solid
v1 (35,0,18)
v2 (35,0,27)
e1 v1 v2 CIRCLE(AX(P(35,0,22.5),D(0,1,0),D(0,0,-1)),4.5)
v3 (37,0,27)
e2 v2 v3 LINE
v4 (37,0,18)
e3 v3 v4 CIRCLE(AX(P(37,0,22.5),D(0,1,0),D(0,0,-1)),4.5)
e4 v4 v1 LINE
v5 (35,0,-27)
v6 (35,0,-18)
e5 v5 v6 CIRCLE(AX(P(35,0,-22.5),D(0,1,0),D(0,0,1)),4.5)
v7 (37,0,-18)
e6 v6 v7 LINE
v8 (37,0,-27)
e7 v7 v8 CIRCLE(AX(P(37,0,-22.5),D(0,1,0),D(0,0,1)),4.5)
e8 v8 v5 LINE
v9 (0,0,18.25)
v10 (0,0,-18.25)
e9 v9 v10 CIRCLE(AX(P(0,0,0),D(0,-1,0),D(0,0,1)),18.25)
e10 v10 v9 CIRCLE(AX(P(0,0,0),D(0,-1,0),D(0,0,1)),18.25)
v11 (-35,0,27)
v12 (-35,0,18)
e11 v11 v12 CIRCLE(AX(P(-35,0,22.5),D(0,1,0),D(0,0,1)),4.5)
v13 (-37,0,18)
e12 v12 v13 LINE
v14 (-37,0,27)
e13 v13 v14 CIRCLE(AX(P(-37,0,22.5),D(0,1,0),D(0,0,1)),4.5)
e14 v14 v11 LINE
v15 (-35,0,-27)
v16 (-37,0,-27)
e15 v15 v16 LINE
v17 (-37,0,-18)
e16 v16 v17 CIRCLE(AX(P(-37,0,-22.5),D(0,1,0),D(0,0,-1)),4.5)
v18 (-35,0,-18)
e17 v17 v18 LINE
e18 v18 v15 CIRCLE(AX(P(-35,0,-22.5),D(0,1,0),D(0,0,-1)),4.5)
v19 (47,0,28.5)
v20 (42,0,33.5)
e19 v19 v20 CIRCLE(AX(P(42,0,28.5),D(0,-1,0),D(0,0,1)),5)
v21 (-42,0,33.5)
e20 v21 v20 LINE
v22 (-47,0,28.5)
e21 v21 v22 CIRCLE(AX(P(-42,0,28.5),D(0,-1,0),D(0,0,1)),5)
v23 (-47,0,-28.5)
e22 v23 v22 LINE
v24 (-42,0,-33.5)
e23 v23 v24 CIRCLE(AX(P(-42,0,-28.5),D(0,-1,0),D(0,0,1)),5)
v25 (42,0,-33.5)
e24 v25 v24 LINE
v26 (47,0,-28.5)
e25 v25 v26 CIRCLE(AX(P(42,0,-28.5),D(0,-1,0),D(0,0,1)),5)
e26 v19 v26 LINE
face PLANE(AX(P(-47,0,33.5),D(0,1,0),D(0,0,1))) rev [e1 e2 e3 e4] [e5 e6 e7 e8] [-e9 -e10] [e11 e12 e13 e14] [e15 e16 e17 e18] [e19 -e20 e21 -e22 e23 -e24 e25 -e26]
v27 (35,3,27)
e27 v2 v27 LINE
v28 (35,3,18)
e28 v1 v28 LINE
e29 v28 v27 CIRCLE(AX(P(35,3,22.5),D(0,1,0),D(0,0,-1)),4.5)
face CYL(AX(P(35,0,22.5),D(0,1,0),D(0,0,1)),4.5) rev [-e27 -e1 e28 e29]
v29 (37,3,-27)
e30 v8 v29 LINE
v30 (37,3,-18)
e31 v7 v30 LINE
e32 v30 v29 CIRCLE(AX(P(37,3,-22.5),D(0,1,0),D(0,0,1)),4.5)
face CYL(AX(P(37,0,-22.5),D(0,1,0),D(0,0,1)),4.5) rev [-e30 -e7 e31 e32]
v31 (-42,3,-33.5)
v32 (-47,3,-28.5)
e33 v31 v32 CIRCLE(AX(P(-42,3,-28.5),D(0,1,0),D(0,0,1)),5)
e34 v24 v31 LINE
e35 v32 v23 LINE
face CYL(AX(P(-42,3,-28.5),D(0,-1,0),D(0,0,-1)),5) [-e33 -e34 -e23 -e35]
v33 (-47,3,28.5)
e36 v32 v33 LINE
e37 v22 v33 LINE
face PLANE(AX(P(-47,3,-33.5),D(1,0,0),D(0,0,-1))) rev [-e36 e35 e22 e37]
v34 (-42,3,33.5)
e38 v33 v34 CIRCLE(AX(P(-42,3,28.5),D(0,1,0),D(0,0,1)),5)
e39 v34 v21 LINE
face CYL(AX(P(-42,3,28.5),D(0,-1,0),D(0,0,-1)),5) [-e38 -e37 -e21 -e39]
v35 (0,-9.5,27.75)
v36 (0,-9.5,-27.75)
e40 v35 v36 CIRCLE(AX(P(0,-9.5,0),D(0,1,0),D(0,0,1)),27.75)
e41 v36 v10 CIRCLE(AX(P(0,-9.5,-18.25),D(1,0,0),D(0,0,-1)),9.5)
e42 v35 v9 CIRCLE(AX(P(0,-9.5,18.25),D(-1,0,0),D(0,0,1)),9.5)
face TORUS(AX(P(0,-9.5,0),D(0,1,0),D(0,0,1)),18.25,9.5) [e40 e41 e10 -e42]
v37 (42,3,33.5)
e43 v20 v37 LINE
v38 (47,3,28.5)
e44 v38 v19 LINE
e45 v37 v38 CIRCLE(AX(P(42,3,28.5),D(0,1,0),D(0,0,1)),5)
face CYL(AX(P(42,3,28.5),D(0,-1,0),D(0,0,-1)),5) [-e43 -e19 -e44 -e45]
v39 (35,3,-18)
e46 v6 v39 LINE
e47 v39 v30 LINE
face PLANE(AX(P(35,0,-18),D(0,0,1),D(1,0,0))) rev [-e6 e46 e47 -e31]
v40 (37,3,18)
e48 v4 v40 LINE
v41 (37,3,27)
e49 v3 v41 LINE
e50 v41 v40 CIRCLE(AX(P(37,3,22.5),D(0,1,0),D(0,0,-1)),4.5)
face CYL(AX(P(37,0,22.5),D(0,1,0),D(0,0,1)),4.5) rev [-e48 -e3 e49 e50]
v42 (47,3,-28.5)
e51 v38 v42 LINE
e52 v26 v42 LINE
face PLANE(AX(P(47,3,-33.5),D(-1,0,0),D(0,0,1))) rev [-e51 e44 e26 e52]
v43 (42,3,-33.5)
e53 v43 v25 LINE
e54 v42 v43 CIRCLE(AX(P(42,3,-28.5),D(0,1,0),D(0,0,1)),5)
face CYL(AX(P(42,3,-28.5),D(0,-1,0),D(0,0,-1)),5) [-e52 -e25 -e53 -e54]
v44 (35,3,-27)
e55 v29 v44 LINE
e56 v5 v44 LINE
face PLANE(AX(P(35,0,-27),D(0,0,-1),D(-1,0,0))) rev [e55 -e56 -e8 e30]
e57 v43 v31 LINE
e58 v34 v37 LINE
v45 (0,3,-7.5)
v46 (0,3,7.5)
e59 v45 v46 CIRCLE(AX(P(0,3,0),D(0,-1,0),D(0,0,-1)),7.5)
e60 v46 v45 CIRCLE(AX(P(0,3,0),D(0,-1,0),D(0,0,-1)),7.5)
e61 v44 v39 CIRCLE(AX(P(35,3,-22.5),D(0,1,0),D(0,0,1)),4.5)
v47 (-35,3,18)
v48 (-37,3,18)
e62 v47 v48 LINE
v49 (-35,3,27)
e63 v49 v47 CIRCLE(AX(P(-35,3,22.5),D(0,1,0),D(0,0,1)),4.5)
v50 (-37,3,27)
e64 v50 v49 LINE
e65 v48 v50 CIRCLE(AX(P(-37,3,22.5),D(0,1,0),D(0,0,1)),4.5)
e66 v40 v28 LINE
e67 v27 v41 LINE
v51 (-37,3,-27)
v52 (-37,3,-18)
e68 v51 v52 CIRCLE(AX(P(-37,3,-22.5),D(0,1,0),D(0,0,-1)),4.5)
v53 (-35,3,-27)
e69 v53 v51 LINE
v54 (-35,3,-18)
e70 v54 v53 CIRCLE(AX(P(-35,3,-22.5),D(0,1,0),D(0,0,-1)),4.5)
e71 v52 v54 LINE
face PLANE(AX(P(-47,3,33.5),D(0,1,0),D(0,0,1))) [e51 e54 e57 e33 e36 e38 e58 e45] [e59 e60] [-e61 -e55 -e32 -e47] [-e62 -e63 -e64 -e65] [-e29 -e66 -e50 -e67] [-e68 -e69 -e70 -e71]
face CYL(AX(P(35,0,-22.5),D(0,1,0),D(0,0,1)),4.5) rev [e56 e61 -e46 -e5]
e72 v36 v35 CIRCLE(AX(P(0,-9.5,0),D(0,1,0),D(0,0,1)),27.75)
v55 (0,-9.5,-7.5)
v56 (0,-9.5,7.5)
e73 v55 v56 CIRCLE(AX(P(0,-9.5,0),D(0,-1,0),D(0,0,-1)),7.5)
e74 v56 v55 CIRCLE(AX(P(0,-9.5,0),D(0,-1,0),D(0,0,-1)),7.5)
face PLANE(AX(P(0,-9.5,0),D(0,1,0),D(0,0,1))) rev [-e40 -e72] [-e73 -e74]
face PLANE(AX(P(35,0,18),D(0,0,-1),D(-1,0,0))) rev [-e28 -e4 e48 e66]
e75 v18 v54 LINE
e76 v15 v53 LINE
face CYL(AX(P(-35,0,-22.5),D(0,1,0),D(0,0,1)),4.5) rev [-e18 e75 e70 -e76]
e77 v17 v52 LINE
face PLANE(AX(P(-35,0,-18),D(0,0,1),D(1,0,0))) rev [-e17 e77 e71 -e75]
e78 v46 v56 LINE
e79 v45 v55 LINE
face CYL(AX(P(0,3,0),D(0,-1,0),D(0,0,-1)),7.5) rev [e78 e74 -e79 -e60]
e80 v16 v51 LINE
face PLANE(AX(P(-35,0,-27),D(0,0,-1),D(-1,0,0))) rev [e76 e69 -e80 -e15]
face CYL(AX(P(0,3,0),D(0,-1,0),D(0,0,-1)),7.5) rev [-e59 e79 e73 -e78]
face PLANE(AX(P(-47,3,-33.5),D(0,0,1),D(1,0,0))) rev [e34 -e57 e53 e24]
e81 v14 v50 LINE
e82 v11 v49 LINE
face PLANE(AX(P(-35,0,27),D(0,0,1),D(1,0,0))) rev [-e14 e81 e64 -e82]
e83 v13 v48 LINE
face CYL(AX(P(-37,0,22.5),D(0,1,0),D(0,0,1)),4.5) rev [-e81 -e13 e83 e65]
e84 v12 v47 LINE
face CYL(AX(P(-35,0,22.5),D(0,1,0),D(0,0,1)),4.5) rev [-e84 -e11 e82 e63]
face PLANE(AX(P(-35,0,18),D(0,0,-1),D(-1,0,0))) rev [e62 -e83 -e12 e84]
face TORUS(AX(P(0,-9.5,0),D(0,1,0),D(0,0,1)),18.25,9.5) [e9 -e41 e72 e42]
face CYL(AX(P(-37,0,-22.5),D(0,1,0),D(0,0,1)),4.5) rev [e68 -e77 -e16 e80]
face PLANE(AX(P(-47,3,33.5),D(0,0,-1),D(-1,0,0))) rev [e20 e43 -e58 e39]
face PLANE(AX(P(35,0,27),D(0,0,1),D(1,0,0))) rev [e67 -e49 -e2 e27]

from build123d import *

# Parameters (mm, degrees)
SKETCH_2_W          = 94
SKETCH_2_H          = 67
EXTRUDE_1_DEPTH     = 3
FILLET_1_R          = 5
CUT_EXTRUDE_1_DEPTH = 58.794895968
SKETCH_6_R          = 7.5
CUT_EXTRUDE_2_DEPTH = 60.055059055


with BuildPart() as part:
    # 草图2 → 拉伸1 (new body)
    with BuildSketch(Plane(origin=(0, 0, 0), x_dir=(1, 0, 0), z_dir=(0, 1, 0))):
        Rectangle(SKETCH_2_W, SKETCH_2_H)
    extrude(amount=EXTRUDE_1_DEPTH)

    # 圆角1
    fillet_1_edges = [part.edges().sort_by_distance(p)[0] for p in [
        (-47, 1.5, -33.5),
        (47, 1.5, -33.5),
        (47, 1.5, 33.5),
        (-47, 1.5, 33.5),
    ]]
    fillet(fillet_1_edges, radius=FILLET_1_R)

    # 草图3 → 切除-拉伸1 (cut, through all)
    with BuildSketch(Plane(origin=(0, 3, 0), x_dir=(-1, 0, 0), z_dir=(0, 1, 0))):
        with BuildLine():
            Line((35, 27), (37, 27))
            ThreePointArc((37, 27), (41.5, 22.5), (37, 18))
            Line((37, 18), (35, 18))
            ThreePointArc((35, 18), (30.5, 22.5), (35, 27))
        make_face()
        with BuildLine():
            Line((-35, 18), (-37, 18))
            ThreePointArc((-37, 18), (-41.5, 22.5), (-37, 27))
            Line((-37, 27), (-35, 27))
            ThreePointArc((-35, 27), (-30.5, 22.5), (-35, 18))
        make_face()
        with BuildLine():
            Line((-35, -27), (-37, -27))
            ThreePointArc((-37, -27), (-41.5, -22.5), (-37, -18))
            Line((-37, -18), (-35, -18))
            ThreePointArc((-35, -18), (-30.5, -22.5), (-35, -27))
        make_face()
        with BuildLine():
            Line((35, -18), (37, -18))
            ThreePointArc((37, -18), (41.5, -22.5), (37, -27))
            Line((37, -27), (35, -27))
            ThreePointArc((35, -27), (30.5, -22.5), (35, -18))
        make_face()
    extrude(amount=-CUT_EXTRUDE_1_DEPTH, mode=Mode.SUBTRACT)

    # 草图4 → 旋转1 (revolve)
    with BuildSketch(Plane.XY, mode=Mode.PRIVATE) as revolve_1_sk:
        with BuildLine():
            Line((0, -9.5), (27.75, -9.5))
            ThreePointArc((27.75, -9.5), (24.967514421, -2.782485579), (18.25, 0))
            Line((18.25, 0), (0, 0))
            Line((0, 0), (0, -9.5))
        make_face()
    revolve(revolve_1_sk.sketch.rotate(Axis((0, 11.062770563, 0), (0, -1, 0)), 90), axis=Axis((0, 11.062770563, 0), (0, -1, 0)))

    # 草图6 → 切除-拉伸2 (cut, through all)
    with BuildSketch(Plane.XZ.offset(9.5)):
        with Locations(Location((0, 0, 0), (0, 0, 270))):
            Circle(SKETCH_6_R)
    extrude(amount=-CUT_EXTRUDE_2_DEPTH, mode=Mode.SUBTRACT)


solid = part.part
